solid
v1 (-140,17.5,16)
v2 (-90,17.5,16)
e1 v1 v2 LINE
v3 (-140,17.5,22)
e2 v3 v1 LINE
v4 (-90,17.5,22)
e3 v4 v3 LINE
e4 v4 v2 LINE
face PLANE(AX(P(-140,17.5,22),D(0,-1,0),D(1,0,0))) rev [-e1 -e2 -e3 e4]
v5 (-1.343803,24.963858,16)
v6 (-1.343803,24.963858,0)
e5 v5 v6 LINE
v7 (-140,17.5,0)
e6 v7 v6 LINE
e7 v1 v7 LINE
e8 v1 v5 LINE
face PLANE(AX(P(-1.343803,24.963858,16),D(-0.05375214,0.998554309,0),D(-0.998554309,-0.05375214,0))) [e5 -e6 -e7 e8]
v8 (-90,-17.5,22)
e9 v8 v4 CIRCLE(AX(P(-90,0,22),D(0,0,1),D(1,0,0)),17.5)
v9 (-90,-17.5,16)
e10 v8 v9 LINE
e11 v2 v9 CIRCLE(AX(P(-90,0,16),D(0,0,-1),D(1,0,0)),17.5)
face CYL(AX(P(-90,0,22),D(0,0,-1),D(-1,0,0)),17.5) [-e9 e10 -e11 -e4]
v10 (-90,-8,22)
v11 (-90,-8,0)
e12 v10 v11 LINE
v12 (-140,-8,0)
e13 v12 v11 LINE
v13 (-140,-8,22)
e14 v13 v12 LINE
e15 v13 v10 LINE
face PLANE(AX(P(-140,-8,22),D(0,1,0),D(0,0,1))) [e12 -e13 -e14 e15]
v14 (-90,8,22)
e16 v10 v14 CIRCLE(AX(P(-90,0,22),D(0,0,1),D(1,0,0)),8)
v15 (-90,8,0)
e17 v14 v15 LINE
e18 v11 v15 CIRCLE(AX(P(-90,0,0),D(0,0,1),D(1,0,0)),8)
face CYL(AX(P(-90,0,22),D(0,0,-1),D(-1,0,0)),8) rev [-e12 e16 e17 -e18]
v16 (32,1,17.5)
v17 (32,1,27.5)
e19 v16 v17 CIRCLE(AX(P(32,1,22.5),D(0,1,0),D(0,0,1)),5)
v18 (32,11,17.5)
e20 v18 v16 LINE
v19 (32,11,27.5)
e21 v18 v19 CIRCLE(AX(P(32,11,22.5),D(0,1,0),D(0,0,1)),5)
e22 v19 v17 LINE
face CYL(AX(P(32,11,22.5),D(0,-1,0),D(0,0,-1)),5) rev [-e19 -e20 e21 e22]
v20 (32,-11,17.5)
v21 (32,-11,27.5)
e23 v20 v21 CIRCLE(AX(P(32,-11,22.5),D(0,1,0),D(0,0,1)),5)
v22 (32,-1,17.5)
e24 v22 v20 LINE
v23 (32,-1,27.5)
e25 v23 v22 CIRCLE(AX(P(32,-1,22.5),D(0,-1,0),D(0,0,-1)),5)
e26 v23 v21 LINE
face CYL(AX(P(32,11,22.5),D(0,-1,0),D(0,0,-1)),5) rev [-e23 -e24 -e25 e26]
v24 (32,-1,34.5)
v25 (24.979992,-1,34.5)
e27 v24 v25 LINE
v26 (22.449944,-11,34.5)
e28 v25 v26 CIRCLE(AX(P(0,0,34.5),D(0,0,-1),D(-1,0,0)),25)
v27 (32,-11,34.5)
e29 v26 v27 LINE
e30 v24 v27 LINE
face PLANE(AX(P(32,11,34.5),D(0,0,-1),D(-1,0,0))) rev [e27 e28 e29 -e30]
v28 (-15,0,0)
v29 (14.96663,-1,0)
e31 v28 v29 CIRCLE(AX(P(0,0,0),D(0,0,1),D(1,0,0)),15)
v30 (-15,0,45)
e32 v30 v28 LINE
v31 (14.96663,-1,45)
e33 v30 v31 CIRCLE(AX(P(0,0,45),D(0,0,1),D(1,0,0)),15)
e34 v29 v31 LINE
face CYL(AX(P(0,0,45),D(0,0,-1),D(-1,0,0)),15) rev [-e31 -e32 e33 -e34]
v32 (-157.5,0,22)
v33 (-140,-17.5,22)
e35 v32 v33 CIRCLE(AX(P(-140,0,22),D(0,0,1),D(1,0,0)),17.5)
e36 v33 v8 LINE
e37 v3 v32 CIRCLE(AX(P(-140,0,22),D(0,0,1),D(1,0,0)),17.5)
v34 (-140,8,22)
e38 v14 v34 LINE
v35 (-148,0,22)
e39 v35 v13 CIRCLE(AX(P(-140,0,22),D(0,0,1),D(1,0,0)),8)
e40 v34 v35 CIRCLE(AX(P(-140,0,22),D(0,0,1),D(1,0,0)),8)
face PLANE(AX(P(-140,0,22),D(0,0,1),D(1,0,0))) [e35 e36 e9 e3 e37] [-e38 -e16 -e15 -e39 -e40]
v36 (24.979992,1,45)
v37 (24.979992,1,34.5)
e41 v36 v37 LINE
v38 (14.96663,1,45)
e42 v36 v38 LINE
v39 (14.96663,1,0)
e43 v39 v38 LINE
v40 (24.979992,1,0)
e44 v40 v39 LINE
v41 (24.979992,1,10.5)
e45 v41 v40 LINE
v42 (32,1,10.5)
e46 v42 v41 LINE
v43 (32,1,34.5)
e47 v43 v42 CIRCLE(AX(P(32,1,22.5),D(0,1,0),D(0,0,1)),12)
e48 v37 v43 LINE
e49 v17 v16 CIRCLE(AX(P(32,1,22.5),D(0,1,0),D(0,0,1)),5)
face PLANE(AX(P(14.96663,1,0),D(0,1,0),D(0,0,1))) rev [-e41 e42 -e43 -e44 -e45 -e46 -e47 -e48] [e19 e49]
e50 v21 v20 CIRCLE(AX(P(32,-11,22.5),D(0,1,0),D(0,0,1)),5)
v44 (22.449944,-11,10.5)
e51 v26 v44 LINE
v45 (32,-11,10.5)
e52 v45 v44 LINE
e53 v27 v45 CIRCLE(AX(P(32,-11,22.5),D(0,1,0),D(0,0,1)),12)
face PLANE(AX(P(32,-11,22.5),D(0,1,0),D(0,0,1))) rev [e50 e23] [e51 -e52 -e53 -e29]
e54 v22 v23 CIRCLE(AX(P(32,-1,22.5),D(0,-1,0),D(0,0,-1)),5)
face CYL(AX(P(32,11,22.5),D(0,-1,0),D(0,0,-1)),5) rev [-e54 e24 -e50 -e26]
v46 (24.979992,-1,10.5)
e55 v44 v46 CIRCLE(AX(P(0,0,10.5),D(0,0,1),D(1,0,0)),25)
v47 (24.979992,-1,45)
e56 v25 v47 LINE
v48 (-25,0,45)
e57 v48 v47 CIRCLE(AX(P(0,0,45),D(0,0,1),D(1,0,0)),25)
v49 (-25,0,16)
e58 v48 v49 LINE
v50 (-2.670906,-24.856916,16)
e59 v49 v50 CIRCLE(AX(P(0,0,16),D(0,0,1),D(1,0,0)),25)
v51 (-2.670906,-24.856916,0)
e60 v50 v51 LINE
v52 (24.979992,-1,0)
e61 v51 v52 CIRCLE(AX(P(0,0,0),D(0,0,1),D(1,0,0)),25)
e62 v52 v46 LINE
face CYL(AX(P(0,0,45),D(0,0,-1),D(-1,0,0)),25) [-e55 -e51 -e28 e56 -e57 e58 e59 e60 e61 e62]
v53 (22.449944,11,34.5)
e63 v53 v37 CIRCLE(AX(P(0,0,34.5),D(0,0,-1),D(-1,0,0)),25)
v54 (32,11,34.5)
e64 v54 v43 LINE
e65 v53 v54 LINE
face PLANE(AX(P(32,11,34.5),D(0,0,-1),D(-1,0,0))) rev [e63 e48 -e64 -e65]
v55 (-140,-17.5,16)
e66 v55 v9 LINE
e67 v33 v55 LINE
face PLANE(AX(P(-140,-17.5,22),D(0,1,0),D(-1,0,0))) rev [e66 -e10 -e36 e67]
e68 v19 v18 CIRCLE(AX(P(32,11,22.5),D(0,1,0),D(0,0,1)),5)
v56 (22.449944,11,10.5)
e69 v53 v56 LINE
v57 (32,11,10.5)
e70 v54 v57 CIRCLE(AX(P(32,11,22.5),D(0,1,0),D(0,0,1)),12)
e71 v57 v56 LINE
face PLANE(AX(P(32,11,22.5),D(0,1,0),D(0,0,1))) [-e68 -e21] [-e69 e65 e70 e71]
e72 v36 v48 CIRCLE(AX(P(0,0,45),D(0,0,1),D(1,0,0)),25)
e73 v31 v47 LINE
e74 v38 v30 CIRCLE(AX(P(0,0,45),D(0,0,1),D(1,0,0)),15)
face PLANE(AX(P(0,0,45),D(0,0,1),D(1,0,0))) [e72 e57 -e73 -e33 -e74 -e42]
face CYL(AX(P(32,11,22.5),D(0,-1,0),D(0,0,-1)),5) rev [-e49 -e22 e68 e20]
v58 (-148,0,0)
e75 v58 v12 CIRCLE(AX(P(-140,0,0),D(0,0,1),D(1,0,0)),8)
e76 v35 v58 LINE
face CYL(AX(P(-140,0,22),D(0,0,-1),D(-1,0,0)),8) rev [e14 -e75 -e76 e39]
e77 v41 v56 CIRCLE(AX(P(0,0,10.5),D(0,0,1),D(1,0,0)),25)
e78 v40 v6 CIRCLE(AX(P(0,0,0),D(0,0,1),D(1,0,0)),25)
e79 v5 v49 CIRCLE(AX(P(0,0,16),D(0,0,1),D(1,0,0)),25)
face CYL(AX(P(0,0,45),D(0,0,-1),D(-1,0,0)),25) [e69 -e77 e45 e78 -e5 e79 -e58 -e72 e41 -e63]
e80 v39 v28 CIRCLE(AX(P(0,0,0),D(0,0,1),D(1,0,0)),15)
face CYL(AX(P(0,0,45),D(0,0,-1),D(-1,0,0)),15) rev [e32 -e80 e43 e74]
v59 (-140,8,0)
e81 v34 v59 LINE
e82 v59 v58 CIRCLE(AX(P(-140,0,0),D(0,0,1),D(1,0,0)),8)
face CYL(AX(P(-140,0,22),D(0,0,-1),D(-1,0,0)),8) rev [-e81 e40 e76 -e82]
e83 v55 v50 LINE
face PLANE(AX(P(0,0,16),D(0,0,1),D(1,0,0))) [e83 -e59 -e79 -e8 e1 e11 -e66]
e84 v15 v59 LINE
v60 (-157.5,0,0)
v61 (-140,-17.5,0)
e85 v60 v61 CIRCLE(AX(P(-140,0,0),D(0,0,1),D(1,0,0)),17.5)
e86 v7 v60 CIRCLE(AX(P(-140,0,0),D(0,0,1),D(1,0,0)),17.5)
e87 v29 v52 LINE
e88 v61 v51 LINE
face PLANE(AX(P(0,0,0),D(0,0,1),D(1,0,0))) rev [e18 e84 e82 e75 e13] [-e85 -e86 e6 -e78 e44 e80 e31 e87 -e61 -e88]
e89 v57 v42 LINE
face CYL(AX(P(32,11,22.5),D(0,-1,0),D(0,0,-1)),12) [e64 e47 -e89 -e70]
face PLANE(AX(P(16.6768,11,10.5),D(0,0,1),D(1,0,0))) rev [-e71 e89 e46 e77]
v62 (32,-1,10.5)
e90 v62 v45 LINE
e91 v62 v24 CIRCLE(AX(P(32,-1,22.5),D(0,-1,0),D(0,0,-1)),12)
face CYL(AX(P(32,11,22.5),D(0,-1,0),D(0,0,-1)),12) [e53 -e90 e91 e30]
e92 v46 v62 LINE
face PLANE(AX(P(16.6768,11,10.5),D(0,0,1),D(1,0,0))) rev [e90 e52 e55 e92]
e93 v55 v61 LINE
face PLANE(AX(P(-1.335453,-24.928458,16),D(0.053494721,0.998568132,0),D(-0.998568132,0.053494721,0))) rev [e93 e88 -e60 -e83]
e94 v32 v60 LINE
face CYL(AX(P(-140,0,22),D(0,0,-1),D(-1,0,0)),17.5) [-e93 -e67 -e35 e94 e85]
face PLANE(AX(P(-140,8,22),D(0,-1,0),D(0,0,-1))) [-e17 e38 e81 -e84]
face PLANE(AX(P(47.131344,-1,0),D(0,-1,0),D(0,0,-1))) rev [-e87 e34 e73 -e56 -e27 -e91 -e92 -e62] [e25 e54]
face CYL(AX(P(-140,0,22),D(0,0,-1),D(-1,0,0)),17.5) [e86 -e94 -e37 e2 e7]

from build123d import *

# Parameters (mm, degrees)
HUB_PROFILE_SKETCH_R       = 25
HUB_PROFILE_SKETCH_R_2     = 15
SHAFT_HUB_50_BORE_30_DEPTH = 45
SLOTTED_ARM_END_DEPTH      = 22
ARM_WEB_DEPTH              = 16
CLAMP_LUG_SKETCH_R         = 5
CLAMP_LUG_DEPTH            = 11
CLAMP_SLIT_1MM_DEPTH       = 166.699275798


with BuildPart() as part:
    # Hub Profile Sketch → Shaft Hub Ø50 Bore Ø30 (new body)
    with BuildSketch(Plane.XY):
        with Locations(Location((0, 0, 0), (0, 0, 180))):
            Circle(HUB_PROFILE_SKETCH_R)
        with Locations(Location((0, 0, 0), (0, 0, 180))):
            Circle(HUB_PROFILE_SKETCH_R_2, mode=Mode.SUBTRACT)
    extrude(amount=SHAFT_HUB_50_BORE_30_DEPTH)



with BuildPart() as body_2:
    # Slotted End Sketch → Slotted Arm End (new body)
    with BuildSketch(Plane.XY):
        with BuildLine():
            Line((-140, 17.5), (-90, 17.5))
            ThreePointArc((-90, 17.5), (-72.5, 0), (-90, -17.5))
            Line((-90, -17.5), (-140, -17.5))
            ThreePointArc((-140, -17.5), (-157.5, 0), (-140, 17.5))
        make_face()
        with BuildLine():
            Line((-140, 8), (-90, 8))
            ThreePointArc((-90, 8), (-82, 0), (-90, -8))
            Line((-90, -8), (-140, -8))
            ThreePointArc((-140, -8), (-148, 0), (-140, 8))
        make_face(mode=Mode.SUBTRACT)
    extrude(amount=SLOTTED_ARM_END_DEPTH)


with BuildPart() as part_1:
    add(part.part)

    add(body_2.part)  # Arm Web merges body 2
    # Arm Web Sketch → Arm Web (add)
    with BuildSketch(Plane.XY):
        with BuildLine():
            Line((-1.3438035, 24.963857718), (-140, 17.5))
            Line((-140, 17.5), (-90, 17.5))
            ThreePointArc((-90, 17.5), (-72.5, 0), (-90, -17.5))
            Line((-90, -17.5), (-140, -17.5))
            Line((-140, -17.5), (-2.6709062, -24.856915739))
            ThreePointArc((-2.6709062, -24.856915739), (-24.991135237, 0.665702292), (-1.3438035, 24.963857718))
        make_face()
    extrude(amount=ARM_WEB_DEPTH)

    # Clamp Lug Sketch → Clamp Lug (add, symmetric)
    with BuildSketch(Plane(origin=(0, 0, 0), x_dir=(1, 0, 0), z_dir=(0, 1, 0))):
        with BuildLine():
            Line((32, -34.5), (25, -34.5))
            Line((25, -34.5), (16.676799829, -34.5))
            Line((16.676799829, -34.5), (16.676799829, -10.5))
            Line((16.676799829, -10.5), (25, -10.5))
            Line((25, -10.5), (32, -10.5))
            ThreePointArc((32, -10.5), (44, -22.5), (32, -34.5))
        make_face()
        with Locations(Location((32, -22.5, 0), (0, 0, 270))):
            Circle(CLAMP_LUG_SKETCH_R, mode=Mode.SUBTRACT)
    extrude(amount=CLAMP_LUG_DEPTH, both=True)

    # Clamp Slit Sketch → Clamp Slit 1mm (cut, through all)
    with BuildSketch(Plane.XY.offset(45)):
        with BuildLine():
            Line((14.966629547, -1), (44, -1))
            Line((44, -1), (47.131344101, -1))
            Line((47.131344101, -1), (47.131344101, 1))
            Line((47.131344101, 1), (43.927311634, 1))
            Line((43.927311634, 1), (14.966629547, 1))
            ThreePointArc((14.966629547, 1), (15, 0), (14.966629547, -1))
        make_face()
    extrude(amount=-CLAMP_SLIT_1MM_DEPTH, mode=Mode.SUBTRACT)


solid = part_1.part
